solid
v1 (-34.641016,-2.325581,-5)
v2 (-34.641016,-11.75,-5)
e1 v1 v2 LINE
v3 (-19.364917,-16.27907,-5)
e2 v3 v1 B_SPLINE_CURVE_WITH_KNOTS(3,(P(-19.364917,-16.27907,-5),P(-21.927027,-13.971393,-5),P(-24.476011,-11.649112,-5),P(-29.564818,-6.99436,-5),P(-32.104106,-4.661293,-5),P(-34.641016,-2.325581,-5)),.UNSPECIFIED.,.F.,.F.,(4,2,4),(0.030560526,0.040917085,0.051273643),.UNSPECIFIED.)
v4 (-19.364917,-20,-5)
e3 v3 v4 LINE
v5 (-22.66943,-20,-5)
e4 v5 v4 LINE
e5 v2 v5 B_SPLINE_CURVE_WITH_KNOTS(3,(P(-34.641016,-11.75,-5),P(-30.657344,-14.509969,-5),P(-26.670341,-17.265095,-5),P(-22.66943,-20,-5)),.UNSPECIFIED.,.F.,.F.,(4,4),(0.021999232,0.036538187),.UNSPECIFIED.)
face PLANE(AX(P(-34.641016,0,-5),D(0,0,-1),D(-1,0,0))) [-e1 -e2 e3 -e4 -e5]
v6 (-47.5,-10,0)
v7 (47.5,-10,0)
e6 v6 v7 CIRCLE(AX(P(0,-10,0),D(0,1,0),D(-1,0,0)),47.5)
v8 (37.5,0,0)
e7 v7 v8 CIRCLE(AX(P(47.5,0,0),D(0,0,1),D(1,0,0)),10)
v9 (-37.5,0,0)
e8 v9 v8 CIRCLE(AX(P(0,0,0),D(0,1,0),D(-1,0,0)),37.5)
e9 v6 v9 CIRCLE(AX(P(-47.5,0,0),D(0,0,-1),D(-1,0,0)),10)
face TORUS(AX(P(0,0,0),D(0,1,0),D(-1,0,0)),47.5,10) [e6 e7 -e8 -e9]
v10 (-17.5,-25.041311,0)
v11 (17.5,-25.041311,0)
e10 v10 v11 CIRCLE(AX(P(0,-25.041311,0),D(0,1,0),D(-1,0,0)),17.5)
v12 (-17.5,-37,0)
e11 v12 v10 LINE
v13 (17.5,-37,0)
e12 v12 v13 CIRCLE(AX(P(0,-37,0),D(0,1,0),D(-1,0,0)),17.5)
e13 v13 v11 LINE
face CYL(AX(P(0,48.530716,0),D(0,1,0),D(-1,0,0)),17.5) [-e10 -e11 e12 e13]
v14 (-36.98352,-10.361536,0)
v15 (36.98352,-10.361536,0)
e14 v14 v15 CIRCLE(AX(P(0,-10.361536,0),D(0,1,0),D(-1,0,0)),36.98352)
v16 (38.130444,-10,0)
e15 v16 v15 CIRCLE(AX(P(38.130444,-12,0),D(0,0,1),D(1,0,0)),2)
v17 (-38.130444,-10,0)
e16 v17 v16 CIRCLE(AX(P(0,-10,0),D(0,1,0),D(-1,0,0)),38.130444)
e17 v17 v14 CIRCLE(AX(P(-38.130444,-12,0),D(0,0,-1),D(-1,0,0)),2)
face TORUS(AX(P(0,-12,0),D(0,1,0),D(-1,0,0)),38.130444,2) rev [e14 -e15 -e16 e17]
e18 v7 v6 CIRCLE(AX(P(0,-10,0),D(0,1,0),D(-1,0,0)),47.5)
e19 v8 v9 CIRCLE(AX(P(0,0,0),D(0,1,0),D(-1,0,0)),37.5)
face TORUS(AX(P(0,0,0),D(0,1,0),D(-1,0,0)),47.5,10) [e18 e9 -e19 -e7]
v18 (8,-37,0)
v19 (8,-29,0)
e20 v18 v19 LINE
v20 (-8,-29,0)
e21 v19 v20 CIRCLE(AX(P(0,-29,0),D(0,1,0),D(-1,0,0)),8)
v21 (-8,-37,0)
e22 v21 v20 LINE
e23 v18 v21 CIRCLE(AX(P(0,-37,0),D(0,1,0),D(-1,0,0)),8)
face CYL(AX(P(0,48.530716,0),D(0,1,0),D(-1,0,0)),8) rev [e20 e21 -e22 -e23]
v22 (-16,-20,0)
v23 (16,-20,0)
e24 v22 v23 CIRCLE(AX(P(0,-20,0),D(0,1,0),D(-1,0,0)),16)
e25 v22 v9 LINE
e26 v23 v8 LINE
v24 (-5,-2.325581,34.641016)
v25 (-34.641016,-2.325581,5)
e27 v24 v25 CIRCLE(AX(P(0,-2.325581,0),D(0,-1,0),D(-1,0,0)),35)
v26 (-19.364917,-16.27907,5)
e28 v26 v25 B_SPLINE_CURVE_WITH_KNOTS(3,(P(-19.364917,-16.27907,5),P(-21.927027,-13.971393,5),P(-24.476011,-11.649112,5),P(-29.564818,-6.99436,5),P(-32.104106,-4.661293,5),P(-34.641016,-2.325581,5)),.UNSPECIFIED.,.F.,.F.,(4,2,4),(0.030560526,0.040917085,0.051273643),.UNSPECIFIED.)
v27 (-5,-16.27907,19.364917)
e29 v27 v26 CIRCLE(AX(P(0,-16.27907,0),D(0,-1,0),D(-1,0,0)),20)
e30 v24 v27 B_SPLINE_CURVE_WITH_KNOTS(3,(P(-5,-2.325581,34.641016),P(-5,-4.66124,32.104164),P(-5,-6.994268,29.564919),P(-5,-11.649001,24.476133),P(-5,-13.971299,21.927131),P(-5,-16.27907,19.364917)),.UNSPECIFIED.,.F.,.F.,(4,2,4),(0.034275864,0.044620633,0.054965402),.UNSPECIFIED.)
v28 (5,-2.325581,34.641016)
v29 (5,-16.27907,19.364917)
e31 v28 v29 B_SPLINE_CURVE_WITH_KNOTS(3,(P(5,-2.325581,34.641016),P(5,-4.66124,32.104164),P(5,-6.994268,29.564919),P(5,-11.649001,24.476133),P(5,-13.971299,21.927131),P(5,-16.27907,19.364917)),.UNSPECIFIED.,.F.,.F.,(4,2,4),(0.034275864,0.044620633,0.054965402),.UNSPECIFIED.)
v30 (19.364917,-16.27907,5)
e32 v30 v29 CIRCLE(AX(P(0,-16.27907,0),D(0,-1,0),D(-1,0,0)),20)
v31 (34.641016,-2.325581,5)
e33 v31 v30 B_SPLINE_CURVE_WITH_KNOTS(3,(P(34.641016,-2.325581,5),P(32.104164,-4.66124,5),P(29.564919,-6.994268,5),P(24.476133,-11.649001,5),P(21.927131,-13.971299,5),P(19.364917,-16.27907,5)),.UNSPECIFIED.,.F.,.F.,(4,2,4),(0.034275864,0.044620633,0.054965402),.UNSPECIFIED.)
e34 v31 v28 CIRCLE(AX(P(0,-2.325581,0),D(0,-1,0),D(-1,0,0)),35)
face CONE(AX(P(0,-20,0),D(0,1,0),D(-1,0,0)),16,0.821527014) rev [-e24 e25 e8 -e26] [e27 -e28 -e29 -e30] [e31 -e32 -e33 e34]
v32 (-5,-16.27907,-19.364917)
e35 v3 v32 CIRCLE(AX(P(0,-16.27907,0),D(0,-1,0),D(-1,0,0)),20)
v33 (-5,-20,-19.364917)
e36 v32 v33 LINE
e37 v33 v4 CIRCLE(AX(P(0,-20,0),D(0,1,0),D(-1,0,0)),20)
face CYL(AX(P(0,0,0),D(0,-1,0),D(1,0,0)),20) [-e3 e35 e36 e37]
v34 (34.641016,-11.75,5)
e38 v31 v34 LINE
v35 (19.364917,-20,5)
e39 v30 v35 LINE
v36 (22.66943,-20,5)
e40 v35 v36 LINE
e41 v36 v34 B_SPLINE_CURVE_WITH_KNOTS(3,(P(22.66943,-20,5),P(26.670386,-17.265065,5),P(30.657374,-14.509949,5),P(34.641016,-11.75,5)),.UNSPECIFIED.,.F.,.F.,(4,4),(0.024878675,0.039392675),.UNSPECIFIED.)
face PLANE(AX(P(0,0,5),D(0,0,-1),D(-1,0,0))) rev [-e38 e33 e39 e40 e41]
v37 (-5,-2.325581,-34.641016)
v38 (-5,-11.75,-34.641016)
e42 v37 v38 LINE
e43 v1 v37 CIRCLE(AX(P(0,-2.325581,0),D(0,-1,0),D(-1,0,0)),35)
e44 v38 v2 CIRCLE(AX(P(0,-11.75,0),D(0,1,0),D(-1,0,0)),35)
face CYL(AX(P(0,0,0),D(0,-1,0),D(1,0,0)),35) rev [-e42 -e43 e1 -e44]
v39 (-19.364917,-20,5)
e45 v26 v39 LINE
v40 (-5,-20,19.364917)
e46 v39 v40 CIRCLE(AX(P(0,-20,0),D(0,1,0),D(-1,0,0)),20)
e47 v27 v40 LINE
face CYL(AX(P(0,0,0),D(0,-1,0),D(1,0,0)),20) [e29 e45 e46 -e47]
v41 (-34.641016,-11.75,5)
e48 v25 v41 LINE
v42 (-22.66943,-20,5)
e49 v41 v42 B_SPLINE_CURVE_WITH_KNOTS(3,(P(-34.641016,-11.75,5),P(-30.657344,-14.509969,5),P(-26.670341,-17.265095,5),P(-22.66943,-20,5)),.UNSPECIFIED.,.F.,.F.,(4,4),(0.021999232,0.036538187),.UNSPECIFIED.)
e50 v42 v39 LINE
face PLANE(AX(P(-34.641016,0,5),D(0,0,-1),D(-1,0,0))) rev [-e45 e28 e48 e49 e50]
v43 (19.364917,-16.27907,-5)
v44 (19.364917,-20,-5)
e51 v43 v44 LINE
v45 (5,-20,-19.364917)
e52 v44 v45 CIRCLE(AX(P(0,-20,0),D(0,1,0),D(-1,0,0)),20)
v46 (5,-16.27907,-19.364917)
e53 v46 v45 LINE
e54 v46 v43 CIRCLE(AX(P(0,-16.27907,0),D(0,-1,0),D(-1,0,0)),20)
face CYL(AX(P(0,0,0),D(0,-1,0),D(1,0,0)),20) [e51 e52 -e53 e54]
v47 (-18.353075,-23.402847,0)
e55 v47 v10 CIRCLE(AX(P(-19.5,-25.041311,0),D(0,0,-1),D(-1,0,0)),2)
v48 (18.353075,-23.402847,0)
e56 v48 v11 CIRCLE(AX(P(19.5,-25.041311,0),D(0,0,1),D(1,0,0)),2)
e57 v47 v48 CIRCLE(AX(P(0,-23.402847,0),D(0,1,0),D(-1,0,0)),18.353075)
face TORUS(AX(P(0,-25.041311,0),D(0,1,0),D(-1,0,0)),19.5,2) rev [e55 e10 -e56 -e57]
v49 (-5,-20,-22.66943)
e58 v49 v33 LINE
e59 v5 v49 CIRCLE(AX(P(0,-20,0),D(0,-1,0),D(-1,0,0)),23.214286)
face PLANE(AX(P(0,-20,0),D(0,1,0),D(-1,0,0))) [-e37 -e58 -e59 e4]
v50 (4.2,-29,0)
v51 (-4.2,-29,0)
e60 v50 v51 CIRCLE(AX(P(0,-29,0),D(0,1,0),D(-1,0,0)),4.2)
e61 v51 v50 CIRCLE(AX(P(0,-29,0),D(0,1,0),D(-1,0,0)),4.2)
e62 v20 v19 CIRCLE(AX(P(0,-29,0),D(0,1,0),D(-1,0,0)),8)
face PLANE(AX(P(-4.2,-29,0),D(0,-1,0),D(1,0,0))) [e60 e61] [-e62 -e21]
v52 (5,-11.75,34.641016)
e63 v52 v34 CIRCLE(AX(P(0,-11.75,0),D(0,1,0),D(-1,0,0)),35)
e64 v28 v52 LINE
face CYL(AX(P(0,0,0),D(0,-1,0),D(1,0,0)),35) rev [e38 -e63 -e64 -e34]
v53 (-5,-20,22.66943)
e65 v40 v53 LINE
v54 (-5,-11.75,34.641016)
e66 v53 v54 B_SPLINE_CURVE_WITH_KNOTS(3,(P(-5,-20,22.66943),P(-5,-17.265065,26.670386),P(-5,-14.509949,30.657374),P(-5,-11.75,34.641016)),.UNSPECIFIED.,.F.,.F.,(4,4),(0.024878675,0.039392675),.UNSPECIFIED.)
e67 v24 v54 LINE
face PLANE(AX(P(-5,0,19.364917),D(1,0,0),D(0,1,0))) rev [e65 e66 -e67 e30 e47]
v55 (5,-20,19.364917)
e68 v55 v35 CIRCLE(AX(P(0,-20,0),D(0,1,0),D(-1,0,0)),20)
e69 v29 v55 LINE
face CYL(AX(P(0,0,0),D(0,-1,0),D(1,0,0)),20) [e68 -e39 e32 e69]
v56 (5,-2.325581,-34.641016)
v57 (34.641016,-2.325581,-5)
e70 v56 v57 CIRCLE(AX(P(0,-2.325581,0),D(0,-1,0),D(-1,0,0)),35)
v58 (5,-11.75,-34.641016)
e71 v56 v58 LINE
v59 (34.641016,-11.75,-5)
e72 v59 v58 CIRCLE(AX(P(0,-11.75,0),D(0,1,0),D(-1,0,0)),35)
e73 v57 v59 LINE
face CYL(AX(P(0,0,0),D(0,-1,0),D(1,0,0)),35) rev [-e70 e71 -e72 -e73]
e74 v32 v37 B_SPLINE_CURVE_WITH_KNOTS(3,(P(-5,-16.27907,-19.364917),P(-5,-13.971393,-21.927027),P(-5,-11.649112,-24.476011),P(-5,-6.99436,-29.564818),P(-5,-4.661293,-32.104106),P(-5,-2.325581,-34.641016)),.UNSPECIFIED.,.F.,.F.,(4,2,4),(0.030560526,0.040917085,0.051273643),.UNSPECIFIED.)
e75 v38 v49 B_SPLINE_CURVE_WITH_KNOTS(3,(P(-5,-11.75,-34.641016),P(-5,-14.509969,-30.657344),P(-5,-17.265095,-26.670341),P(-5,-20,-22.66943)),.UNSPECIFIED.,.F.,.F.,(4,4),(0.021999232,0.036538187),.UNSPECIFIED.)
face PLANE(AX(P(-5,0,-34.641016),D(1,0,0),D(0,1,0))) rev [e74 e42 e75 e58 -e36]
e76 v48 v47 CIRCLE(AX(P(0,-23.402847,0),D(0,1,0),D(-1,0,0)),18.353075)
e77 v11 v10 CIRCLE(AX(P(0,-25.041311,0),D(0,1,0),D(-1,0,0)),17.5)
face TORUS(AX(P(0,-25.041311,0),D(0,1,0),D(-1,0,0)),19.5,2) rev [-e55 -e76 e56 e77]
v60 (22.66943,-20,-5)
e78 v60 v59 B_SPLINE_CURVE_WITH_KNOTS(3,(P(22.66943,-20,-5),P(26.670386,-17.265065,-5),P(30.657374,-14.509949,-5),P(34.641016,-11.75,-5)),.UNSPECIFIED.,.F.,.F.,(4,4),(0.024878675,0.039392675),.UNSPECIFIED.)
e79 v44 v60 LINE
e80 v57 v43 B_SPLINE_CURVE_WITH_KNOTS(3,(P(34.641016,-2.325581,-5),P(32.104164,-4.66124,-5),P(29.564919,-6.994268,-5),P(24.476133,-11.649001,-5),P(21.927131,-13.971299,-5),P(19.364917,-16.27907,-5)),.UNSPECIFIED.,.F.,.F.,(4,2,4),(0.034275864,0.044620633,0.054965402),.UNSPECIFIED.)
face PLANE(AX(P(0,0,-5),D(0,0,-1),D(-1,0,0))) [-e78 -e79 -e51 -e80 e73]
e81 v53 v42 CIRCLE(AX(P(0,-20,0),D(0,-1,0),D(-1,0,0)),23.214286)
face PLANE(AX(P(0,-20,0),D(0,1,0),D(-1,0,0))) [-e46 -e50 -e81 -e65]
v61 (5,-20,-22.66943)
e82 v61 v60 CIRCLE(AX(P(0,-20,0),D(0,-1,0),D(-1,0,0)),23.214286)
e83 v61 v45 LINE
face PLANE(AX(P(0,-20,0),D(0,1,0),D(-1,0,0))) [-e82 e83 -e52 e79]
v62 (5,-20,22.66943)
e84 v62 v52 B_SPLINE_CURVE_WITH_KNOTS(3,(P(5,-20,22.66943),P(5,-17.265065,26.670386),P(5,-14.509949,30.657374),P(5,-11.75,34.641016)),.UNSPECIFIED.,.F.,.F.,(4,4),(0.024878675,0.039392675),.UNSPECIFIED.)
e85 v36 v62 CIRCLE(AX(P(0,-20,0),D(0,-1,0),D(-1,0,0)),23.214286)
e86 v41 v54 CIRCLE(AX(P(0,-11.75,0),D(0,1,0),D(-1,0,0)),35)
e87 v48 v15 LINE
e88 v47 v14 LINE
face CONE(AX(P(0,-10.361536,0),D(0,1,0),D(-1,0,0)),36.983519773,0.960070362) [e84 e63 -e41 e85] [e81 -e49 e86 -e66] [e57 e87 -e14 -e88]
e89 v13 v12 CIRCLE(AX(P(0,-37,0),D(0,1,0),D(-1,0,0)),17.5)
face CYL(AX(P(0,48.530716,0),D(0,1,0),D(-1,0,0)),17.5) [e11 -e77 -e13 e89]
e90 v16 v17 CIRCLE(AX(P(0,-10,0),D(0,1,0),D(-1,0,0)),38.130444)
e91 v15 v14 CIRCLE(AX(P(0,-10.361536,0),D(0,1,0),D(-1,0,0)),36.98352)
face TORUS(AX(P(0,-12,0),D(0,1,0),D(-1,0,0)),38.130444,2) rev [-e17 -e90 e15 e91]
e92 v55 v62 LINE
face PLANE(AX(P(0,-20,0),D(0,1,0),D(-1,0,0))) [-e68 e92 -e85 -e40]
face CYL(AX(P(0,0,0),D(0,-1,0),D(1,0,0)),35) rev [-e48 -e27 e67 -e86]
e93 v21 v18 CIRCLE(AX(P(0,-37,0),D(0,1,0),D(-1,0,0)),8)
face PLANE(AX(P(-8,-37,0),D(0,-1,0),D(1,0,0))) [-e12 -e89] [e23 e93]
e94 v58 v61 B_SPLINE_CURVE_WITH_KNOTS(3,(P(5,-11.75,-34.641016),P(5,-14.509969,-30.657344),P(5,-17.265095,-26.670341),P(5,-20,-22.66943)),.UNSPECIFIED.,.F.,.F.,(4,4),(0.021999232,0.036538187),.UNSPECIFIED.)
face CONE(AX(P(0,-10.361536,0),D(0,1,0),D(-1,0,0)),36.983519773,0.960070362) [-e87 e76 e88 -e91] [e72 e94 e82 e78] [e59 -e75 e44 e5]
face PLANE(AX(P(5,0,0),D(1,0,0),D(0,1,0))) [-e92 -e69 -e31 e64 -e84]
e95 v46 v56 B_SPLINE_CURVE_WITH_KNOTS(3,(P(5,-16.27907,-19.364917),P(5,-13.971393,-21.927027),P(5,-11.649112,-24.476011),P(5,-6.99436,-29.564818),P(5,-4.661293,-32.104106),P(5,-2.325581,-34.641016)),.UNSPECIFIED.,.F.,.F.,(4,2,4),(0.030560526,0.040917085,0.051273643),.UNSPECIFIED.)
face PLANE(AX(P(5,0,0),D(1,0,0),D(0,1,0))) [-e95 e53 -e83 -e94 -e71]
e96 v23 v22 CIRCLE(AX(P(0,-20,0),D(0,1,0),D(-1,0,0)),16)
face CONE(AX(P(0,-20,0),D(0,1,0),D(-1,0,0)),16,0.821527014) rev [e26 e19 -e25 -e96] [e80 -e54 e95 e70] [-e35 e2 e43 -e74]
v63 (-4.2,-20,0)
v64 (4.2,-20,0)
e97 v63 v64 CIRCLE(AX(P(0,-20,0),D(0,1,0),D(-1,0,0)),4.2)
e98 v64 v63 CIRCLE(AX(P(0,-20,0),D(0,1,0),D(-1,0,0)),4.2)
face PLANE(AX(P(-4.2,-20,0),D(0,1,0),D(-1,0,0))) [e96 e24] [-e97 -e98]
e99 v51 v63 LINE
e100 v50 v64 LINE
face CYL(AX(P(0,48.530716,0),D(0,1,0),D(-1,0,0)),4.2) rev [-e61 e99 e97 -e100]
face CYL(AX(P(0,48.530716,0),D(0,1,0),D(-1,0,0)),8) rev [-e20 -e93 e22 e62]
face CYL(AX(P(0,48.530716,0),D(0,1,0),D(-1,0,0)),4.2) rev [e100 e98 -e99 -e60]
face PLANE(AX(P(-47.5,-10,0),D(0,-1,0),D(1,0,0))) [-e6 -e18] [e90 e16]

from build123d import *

# Parameters (mm, degrees)
SPOKE_WINDOWS_4X_DEPTH = 20


with BuildPart() as part:
    # Handwheel Profile Sketch → Handwheel Body (revolve)
    with BuildSketch(Plane.XY):
        with BuildLine():
            Line((-8, -37), (-17.5, -37))
            Line((-17.5, -37), (-17.5, -25.041311123))
            ThreePointArc((-17.5, -25.041311123), (-17.726042647, -24.117690362), (-18.353075311, -23.402847282))
            Line((-18.353075311, -23.402847282), (-36.983519773, -10.361536159))
            ThreePointArc((-36.983519773, -10.361536159), (-37.529165692, -10.092524223), (-38.130444462, -10))
            Line((-38.130444462, -10), (-47.5, -10))
            ThreePointArc((-47.5, -10), (-54.571067812, 7.071067812), (-37.5, 0))
            Line((-37.5, 0), (-16, -20))
            Line((-16, -20), (-4.2, -20))
            Line((-4.2, -20), (-4.2, -29))
            Line((-4.2, -29), (-8, -29))
            Line((-8, -29), (-8, -37))
        make_face()
    revolve(axis=Axis((0, 48.530715578, 0), (0, -1, 0)))

    # Spoke Windows Sketch → Spoke Windows 4x (cut)
    with BuildSketch(Plane(origin=(0, -20, 0), x_dir=(1, 0, 0), z_dir=(0, 1, 0))):
        with BuildLine():
            Line((19.364916731, 5), (34.641016151, 5))
            ThreePointArc((34.641016151, 5), (24.748737342, 24.748737342), (5, 34.641016151))
            Line((5, 34.641016151), (5, 19.364916731))
            ThreePointArc((5, 19.364916731), (14.142135624, 14.142135624), (19.364916731, 5))
        make_face()
        with BuildLine():
            Line((34.641016151, -5), (19.364916731, -5))
            ThreePointArc((19.364916731, -5), (14.142135624, -14.142135624), (5, -19.364916731))
            Line((5, -19.364916731), (5, -34.641016151))
            ThreePointArc((5, -34.641016151), (24.748737342, -24.748737342), (34.641016151, -5))
        make_face()
        with BuildLine():
            ThreePointArc((-5, 34.641016151), (-24.748737342, 24.748737342), (-34.641016151, 5))
            Line((-34.641016151, 5), (-19.364916731, 5))
            ThreePointArc((-19.364916731, 5), (-14.142135624, 14.142135624), (-5, 19.364916731))
            Line((-5, 19.364916731), (-5, 34.641016151))
        make_face()
        with BuildLine():
            ThreePointArc((-34.641016151, -5), (-24.748737342, -24.748737342), (-5, -34.641016151))
            Line((-5, -34.641016151), (-5, -19.364916731))
            ThreePointArc((-5, -19.364916731), (-14.142135624, -14.142135624), (-19.364916731, -5))
            Line((-19.364916731, -5), (-34.641016151, -5))
        make_face()
    extrude(amount=SPOKE_WINDOWS_4X_DEPTH, mode=Mode.SUBTRACT)


solid = part.part
